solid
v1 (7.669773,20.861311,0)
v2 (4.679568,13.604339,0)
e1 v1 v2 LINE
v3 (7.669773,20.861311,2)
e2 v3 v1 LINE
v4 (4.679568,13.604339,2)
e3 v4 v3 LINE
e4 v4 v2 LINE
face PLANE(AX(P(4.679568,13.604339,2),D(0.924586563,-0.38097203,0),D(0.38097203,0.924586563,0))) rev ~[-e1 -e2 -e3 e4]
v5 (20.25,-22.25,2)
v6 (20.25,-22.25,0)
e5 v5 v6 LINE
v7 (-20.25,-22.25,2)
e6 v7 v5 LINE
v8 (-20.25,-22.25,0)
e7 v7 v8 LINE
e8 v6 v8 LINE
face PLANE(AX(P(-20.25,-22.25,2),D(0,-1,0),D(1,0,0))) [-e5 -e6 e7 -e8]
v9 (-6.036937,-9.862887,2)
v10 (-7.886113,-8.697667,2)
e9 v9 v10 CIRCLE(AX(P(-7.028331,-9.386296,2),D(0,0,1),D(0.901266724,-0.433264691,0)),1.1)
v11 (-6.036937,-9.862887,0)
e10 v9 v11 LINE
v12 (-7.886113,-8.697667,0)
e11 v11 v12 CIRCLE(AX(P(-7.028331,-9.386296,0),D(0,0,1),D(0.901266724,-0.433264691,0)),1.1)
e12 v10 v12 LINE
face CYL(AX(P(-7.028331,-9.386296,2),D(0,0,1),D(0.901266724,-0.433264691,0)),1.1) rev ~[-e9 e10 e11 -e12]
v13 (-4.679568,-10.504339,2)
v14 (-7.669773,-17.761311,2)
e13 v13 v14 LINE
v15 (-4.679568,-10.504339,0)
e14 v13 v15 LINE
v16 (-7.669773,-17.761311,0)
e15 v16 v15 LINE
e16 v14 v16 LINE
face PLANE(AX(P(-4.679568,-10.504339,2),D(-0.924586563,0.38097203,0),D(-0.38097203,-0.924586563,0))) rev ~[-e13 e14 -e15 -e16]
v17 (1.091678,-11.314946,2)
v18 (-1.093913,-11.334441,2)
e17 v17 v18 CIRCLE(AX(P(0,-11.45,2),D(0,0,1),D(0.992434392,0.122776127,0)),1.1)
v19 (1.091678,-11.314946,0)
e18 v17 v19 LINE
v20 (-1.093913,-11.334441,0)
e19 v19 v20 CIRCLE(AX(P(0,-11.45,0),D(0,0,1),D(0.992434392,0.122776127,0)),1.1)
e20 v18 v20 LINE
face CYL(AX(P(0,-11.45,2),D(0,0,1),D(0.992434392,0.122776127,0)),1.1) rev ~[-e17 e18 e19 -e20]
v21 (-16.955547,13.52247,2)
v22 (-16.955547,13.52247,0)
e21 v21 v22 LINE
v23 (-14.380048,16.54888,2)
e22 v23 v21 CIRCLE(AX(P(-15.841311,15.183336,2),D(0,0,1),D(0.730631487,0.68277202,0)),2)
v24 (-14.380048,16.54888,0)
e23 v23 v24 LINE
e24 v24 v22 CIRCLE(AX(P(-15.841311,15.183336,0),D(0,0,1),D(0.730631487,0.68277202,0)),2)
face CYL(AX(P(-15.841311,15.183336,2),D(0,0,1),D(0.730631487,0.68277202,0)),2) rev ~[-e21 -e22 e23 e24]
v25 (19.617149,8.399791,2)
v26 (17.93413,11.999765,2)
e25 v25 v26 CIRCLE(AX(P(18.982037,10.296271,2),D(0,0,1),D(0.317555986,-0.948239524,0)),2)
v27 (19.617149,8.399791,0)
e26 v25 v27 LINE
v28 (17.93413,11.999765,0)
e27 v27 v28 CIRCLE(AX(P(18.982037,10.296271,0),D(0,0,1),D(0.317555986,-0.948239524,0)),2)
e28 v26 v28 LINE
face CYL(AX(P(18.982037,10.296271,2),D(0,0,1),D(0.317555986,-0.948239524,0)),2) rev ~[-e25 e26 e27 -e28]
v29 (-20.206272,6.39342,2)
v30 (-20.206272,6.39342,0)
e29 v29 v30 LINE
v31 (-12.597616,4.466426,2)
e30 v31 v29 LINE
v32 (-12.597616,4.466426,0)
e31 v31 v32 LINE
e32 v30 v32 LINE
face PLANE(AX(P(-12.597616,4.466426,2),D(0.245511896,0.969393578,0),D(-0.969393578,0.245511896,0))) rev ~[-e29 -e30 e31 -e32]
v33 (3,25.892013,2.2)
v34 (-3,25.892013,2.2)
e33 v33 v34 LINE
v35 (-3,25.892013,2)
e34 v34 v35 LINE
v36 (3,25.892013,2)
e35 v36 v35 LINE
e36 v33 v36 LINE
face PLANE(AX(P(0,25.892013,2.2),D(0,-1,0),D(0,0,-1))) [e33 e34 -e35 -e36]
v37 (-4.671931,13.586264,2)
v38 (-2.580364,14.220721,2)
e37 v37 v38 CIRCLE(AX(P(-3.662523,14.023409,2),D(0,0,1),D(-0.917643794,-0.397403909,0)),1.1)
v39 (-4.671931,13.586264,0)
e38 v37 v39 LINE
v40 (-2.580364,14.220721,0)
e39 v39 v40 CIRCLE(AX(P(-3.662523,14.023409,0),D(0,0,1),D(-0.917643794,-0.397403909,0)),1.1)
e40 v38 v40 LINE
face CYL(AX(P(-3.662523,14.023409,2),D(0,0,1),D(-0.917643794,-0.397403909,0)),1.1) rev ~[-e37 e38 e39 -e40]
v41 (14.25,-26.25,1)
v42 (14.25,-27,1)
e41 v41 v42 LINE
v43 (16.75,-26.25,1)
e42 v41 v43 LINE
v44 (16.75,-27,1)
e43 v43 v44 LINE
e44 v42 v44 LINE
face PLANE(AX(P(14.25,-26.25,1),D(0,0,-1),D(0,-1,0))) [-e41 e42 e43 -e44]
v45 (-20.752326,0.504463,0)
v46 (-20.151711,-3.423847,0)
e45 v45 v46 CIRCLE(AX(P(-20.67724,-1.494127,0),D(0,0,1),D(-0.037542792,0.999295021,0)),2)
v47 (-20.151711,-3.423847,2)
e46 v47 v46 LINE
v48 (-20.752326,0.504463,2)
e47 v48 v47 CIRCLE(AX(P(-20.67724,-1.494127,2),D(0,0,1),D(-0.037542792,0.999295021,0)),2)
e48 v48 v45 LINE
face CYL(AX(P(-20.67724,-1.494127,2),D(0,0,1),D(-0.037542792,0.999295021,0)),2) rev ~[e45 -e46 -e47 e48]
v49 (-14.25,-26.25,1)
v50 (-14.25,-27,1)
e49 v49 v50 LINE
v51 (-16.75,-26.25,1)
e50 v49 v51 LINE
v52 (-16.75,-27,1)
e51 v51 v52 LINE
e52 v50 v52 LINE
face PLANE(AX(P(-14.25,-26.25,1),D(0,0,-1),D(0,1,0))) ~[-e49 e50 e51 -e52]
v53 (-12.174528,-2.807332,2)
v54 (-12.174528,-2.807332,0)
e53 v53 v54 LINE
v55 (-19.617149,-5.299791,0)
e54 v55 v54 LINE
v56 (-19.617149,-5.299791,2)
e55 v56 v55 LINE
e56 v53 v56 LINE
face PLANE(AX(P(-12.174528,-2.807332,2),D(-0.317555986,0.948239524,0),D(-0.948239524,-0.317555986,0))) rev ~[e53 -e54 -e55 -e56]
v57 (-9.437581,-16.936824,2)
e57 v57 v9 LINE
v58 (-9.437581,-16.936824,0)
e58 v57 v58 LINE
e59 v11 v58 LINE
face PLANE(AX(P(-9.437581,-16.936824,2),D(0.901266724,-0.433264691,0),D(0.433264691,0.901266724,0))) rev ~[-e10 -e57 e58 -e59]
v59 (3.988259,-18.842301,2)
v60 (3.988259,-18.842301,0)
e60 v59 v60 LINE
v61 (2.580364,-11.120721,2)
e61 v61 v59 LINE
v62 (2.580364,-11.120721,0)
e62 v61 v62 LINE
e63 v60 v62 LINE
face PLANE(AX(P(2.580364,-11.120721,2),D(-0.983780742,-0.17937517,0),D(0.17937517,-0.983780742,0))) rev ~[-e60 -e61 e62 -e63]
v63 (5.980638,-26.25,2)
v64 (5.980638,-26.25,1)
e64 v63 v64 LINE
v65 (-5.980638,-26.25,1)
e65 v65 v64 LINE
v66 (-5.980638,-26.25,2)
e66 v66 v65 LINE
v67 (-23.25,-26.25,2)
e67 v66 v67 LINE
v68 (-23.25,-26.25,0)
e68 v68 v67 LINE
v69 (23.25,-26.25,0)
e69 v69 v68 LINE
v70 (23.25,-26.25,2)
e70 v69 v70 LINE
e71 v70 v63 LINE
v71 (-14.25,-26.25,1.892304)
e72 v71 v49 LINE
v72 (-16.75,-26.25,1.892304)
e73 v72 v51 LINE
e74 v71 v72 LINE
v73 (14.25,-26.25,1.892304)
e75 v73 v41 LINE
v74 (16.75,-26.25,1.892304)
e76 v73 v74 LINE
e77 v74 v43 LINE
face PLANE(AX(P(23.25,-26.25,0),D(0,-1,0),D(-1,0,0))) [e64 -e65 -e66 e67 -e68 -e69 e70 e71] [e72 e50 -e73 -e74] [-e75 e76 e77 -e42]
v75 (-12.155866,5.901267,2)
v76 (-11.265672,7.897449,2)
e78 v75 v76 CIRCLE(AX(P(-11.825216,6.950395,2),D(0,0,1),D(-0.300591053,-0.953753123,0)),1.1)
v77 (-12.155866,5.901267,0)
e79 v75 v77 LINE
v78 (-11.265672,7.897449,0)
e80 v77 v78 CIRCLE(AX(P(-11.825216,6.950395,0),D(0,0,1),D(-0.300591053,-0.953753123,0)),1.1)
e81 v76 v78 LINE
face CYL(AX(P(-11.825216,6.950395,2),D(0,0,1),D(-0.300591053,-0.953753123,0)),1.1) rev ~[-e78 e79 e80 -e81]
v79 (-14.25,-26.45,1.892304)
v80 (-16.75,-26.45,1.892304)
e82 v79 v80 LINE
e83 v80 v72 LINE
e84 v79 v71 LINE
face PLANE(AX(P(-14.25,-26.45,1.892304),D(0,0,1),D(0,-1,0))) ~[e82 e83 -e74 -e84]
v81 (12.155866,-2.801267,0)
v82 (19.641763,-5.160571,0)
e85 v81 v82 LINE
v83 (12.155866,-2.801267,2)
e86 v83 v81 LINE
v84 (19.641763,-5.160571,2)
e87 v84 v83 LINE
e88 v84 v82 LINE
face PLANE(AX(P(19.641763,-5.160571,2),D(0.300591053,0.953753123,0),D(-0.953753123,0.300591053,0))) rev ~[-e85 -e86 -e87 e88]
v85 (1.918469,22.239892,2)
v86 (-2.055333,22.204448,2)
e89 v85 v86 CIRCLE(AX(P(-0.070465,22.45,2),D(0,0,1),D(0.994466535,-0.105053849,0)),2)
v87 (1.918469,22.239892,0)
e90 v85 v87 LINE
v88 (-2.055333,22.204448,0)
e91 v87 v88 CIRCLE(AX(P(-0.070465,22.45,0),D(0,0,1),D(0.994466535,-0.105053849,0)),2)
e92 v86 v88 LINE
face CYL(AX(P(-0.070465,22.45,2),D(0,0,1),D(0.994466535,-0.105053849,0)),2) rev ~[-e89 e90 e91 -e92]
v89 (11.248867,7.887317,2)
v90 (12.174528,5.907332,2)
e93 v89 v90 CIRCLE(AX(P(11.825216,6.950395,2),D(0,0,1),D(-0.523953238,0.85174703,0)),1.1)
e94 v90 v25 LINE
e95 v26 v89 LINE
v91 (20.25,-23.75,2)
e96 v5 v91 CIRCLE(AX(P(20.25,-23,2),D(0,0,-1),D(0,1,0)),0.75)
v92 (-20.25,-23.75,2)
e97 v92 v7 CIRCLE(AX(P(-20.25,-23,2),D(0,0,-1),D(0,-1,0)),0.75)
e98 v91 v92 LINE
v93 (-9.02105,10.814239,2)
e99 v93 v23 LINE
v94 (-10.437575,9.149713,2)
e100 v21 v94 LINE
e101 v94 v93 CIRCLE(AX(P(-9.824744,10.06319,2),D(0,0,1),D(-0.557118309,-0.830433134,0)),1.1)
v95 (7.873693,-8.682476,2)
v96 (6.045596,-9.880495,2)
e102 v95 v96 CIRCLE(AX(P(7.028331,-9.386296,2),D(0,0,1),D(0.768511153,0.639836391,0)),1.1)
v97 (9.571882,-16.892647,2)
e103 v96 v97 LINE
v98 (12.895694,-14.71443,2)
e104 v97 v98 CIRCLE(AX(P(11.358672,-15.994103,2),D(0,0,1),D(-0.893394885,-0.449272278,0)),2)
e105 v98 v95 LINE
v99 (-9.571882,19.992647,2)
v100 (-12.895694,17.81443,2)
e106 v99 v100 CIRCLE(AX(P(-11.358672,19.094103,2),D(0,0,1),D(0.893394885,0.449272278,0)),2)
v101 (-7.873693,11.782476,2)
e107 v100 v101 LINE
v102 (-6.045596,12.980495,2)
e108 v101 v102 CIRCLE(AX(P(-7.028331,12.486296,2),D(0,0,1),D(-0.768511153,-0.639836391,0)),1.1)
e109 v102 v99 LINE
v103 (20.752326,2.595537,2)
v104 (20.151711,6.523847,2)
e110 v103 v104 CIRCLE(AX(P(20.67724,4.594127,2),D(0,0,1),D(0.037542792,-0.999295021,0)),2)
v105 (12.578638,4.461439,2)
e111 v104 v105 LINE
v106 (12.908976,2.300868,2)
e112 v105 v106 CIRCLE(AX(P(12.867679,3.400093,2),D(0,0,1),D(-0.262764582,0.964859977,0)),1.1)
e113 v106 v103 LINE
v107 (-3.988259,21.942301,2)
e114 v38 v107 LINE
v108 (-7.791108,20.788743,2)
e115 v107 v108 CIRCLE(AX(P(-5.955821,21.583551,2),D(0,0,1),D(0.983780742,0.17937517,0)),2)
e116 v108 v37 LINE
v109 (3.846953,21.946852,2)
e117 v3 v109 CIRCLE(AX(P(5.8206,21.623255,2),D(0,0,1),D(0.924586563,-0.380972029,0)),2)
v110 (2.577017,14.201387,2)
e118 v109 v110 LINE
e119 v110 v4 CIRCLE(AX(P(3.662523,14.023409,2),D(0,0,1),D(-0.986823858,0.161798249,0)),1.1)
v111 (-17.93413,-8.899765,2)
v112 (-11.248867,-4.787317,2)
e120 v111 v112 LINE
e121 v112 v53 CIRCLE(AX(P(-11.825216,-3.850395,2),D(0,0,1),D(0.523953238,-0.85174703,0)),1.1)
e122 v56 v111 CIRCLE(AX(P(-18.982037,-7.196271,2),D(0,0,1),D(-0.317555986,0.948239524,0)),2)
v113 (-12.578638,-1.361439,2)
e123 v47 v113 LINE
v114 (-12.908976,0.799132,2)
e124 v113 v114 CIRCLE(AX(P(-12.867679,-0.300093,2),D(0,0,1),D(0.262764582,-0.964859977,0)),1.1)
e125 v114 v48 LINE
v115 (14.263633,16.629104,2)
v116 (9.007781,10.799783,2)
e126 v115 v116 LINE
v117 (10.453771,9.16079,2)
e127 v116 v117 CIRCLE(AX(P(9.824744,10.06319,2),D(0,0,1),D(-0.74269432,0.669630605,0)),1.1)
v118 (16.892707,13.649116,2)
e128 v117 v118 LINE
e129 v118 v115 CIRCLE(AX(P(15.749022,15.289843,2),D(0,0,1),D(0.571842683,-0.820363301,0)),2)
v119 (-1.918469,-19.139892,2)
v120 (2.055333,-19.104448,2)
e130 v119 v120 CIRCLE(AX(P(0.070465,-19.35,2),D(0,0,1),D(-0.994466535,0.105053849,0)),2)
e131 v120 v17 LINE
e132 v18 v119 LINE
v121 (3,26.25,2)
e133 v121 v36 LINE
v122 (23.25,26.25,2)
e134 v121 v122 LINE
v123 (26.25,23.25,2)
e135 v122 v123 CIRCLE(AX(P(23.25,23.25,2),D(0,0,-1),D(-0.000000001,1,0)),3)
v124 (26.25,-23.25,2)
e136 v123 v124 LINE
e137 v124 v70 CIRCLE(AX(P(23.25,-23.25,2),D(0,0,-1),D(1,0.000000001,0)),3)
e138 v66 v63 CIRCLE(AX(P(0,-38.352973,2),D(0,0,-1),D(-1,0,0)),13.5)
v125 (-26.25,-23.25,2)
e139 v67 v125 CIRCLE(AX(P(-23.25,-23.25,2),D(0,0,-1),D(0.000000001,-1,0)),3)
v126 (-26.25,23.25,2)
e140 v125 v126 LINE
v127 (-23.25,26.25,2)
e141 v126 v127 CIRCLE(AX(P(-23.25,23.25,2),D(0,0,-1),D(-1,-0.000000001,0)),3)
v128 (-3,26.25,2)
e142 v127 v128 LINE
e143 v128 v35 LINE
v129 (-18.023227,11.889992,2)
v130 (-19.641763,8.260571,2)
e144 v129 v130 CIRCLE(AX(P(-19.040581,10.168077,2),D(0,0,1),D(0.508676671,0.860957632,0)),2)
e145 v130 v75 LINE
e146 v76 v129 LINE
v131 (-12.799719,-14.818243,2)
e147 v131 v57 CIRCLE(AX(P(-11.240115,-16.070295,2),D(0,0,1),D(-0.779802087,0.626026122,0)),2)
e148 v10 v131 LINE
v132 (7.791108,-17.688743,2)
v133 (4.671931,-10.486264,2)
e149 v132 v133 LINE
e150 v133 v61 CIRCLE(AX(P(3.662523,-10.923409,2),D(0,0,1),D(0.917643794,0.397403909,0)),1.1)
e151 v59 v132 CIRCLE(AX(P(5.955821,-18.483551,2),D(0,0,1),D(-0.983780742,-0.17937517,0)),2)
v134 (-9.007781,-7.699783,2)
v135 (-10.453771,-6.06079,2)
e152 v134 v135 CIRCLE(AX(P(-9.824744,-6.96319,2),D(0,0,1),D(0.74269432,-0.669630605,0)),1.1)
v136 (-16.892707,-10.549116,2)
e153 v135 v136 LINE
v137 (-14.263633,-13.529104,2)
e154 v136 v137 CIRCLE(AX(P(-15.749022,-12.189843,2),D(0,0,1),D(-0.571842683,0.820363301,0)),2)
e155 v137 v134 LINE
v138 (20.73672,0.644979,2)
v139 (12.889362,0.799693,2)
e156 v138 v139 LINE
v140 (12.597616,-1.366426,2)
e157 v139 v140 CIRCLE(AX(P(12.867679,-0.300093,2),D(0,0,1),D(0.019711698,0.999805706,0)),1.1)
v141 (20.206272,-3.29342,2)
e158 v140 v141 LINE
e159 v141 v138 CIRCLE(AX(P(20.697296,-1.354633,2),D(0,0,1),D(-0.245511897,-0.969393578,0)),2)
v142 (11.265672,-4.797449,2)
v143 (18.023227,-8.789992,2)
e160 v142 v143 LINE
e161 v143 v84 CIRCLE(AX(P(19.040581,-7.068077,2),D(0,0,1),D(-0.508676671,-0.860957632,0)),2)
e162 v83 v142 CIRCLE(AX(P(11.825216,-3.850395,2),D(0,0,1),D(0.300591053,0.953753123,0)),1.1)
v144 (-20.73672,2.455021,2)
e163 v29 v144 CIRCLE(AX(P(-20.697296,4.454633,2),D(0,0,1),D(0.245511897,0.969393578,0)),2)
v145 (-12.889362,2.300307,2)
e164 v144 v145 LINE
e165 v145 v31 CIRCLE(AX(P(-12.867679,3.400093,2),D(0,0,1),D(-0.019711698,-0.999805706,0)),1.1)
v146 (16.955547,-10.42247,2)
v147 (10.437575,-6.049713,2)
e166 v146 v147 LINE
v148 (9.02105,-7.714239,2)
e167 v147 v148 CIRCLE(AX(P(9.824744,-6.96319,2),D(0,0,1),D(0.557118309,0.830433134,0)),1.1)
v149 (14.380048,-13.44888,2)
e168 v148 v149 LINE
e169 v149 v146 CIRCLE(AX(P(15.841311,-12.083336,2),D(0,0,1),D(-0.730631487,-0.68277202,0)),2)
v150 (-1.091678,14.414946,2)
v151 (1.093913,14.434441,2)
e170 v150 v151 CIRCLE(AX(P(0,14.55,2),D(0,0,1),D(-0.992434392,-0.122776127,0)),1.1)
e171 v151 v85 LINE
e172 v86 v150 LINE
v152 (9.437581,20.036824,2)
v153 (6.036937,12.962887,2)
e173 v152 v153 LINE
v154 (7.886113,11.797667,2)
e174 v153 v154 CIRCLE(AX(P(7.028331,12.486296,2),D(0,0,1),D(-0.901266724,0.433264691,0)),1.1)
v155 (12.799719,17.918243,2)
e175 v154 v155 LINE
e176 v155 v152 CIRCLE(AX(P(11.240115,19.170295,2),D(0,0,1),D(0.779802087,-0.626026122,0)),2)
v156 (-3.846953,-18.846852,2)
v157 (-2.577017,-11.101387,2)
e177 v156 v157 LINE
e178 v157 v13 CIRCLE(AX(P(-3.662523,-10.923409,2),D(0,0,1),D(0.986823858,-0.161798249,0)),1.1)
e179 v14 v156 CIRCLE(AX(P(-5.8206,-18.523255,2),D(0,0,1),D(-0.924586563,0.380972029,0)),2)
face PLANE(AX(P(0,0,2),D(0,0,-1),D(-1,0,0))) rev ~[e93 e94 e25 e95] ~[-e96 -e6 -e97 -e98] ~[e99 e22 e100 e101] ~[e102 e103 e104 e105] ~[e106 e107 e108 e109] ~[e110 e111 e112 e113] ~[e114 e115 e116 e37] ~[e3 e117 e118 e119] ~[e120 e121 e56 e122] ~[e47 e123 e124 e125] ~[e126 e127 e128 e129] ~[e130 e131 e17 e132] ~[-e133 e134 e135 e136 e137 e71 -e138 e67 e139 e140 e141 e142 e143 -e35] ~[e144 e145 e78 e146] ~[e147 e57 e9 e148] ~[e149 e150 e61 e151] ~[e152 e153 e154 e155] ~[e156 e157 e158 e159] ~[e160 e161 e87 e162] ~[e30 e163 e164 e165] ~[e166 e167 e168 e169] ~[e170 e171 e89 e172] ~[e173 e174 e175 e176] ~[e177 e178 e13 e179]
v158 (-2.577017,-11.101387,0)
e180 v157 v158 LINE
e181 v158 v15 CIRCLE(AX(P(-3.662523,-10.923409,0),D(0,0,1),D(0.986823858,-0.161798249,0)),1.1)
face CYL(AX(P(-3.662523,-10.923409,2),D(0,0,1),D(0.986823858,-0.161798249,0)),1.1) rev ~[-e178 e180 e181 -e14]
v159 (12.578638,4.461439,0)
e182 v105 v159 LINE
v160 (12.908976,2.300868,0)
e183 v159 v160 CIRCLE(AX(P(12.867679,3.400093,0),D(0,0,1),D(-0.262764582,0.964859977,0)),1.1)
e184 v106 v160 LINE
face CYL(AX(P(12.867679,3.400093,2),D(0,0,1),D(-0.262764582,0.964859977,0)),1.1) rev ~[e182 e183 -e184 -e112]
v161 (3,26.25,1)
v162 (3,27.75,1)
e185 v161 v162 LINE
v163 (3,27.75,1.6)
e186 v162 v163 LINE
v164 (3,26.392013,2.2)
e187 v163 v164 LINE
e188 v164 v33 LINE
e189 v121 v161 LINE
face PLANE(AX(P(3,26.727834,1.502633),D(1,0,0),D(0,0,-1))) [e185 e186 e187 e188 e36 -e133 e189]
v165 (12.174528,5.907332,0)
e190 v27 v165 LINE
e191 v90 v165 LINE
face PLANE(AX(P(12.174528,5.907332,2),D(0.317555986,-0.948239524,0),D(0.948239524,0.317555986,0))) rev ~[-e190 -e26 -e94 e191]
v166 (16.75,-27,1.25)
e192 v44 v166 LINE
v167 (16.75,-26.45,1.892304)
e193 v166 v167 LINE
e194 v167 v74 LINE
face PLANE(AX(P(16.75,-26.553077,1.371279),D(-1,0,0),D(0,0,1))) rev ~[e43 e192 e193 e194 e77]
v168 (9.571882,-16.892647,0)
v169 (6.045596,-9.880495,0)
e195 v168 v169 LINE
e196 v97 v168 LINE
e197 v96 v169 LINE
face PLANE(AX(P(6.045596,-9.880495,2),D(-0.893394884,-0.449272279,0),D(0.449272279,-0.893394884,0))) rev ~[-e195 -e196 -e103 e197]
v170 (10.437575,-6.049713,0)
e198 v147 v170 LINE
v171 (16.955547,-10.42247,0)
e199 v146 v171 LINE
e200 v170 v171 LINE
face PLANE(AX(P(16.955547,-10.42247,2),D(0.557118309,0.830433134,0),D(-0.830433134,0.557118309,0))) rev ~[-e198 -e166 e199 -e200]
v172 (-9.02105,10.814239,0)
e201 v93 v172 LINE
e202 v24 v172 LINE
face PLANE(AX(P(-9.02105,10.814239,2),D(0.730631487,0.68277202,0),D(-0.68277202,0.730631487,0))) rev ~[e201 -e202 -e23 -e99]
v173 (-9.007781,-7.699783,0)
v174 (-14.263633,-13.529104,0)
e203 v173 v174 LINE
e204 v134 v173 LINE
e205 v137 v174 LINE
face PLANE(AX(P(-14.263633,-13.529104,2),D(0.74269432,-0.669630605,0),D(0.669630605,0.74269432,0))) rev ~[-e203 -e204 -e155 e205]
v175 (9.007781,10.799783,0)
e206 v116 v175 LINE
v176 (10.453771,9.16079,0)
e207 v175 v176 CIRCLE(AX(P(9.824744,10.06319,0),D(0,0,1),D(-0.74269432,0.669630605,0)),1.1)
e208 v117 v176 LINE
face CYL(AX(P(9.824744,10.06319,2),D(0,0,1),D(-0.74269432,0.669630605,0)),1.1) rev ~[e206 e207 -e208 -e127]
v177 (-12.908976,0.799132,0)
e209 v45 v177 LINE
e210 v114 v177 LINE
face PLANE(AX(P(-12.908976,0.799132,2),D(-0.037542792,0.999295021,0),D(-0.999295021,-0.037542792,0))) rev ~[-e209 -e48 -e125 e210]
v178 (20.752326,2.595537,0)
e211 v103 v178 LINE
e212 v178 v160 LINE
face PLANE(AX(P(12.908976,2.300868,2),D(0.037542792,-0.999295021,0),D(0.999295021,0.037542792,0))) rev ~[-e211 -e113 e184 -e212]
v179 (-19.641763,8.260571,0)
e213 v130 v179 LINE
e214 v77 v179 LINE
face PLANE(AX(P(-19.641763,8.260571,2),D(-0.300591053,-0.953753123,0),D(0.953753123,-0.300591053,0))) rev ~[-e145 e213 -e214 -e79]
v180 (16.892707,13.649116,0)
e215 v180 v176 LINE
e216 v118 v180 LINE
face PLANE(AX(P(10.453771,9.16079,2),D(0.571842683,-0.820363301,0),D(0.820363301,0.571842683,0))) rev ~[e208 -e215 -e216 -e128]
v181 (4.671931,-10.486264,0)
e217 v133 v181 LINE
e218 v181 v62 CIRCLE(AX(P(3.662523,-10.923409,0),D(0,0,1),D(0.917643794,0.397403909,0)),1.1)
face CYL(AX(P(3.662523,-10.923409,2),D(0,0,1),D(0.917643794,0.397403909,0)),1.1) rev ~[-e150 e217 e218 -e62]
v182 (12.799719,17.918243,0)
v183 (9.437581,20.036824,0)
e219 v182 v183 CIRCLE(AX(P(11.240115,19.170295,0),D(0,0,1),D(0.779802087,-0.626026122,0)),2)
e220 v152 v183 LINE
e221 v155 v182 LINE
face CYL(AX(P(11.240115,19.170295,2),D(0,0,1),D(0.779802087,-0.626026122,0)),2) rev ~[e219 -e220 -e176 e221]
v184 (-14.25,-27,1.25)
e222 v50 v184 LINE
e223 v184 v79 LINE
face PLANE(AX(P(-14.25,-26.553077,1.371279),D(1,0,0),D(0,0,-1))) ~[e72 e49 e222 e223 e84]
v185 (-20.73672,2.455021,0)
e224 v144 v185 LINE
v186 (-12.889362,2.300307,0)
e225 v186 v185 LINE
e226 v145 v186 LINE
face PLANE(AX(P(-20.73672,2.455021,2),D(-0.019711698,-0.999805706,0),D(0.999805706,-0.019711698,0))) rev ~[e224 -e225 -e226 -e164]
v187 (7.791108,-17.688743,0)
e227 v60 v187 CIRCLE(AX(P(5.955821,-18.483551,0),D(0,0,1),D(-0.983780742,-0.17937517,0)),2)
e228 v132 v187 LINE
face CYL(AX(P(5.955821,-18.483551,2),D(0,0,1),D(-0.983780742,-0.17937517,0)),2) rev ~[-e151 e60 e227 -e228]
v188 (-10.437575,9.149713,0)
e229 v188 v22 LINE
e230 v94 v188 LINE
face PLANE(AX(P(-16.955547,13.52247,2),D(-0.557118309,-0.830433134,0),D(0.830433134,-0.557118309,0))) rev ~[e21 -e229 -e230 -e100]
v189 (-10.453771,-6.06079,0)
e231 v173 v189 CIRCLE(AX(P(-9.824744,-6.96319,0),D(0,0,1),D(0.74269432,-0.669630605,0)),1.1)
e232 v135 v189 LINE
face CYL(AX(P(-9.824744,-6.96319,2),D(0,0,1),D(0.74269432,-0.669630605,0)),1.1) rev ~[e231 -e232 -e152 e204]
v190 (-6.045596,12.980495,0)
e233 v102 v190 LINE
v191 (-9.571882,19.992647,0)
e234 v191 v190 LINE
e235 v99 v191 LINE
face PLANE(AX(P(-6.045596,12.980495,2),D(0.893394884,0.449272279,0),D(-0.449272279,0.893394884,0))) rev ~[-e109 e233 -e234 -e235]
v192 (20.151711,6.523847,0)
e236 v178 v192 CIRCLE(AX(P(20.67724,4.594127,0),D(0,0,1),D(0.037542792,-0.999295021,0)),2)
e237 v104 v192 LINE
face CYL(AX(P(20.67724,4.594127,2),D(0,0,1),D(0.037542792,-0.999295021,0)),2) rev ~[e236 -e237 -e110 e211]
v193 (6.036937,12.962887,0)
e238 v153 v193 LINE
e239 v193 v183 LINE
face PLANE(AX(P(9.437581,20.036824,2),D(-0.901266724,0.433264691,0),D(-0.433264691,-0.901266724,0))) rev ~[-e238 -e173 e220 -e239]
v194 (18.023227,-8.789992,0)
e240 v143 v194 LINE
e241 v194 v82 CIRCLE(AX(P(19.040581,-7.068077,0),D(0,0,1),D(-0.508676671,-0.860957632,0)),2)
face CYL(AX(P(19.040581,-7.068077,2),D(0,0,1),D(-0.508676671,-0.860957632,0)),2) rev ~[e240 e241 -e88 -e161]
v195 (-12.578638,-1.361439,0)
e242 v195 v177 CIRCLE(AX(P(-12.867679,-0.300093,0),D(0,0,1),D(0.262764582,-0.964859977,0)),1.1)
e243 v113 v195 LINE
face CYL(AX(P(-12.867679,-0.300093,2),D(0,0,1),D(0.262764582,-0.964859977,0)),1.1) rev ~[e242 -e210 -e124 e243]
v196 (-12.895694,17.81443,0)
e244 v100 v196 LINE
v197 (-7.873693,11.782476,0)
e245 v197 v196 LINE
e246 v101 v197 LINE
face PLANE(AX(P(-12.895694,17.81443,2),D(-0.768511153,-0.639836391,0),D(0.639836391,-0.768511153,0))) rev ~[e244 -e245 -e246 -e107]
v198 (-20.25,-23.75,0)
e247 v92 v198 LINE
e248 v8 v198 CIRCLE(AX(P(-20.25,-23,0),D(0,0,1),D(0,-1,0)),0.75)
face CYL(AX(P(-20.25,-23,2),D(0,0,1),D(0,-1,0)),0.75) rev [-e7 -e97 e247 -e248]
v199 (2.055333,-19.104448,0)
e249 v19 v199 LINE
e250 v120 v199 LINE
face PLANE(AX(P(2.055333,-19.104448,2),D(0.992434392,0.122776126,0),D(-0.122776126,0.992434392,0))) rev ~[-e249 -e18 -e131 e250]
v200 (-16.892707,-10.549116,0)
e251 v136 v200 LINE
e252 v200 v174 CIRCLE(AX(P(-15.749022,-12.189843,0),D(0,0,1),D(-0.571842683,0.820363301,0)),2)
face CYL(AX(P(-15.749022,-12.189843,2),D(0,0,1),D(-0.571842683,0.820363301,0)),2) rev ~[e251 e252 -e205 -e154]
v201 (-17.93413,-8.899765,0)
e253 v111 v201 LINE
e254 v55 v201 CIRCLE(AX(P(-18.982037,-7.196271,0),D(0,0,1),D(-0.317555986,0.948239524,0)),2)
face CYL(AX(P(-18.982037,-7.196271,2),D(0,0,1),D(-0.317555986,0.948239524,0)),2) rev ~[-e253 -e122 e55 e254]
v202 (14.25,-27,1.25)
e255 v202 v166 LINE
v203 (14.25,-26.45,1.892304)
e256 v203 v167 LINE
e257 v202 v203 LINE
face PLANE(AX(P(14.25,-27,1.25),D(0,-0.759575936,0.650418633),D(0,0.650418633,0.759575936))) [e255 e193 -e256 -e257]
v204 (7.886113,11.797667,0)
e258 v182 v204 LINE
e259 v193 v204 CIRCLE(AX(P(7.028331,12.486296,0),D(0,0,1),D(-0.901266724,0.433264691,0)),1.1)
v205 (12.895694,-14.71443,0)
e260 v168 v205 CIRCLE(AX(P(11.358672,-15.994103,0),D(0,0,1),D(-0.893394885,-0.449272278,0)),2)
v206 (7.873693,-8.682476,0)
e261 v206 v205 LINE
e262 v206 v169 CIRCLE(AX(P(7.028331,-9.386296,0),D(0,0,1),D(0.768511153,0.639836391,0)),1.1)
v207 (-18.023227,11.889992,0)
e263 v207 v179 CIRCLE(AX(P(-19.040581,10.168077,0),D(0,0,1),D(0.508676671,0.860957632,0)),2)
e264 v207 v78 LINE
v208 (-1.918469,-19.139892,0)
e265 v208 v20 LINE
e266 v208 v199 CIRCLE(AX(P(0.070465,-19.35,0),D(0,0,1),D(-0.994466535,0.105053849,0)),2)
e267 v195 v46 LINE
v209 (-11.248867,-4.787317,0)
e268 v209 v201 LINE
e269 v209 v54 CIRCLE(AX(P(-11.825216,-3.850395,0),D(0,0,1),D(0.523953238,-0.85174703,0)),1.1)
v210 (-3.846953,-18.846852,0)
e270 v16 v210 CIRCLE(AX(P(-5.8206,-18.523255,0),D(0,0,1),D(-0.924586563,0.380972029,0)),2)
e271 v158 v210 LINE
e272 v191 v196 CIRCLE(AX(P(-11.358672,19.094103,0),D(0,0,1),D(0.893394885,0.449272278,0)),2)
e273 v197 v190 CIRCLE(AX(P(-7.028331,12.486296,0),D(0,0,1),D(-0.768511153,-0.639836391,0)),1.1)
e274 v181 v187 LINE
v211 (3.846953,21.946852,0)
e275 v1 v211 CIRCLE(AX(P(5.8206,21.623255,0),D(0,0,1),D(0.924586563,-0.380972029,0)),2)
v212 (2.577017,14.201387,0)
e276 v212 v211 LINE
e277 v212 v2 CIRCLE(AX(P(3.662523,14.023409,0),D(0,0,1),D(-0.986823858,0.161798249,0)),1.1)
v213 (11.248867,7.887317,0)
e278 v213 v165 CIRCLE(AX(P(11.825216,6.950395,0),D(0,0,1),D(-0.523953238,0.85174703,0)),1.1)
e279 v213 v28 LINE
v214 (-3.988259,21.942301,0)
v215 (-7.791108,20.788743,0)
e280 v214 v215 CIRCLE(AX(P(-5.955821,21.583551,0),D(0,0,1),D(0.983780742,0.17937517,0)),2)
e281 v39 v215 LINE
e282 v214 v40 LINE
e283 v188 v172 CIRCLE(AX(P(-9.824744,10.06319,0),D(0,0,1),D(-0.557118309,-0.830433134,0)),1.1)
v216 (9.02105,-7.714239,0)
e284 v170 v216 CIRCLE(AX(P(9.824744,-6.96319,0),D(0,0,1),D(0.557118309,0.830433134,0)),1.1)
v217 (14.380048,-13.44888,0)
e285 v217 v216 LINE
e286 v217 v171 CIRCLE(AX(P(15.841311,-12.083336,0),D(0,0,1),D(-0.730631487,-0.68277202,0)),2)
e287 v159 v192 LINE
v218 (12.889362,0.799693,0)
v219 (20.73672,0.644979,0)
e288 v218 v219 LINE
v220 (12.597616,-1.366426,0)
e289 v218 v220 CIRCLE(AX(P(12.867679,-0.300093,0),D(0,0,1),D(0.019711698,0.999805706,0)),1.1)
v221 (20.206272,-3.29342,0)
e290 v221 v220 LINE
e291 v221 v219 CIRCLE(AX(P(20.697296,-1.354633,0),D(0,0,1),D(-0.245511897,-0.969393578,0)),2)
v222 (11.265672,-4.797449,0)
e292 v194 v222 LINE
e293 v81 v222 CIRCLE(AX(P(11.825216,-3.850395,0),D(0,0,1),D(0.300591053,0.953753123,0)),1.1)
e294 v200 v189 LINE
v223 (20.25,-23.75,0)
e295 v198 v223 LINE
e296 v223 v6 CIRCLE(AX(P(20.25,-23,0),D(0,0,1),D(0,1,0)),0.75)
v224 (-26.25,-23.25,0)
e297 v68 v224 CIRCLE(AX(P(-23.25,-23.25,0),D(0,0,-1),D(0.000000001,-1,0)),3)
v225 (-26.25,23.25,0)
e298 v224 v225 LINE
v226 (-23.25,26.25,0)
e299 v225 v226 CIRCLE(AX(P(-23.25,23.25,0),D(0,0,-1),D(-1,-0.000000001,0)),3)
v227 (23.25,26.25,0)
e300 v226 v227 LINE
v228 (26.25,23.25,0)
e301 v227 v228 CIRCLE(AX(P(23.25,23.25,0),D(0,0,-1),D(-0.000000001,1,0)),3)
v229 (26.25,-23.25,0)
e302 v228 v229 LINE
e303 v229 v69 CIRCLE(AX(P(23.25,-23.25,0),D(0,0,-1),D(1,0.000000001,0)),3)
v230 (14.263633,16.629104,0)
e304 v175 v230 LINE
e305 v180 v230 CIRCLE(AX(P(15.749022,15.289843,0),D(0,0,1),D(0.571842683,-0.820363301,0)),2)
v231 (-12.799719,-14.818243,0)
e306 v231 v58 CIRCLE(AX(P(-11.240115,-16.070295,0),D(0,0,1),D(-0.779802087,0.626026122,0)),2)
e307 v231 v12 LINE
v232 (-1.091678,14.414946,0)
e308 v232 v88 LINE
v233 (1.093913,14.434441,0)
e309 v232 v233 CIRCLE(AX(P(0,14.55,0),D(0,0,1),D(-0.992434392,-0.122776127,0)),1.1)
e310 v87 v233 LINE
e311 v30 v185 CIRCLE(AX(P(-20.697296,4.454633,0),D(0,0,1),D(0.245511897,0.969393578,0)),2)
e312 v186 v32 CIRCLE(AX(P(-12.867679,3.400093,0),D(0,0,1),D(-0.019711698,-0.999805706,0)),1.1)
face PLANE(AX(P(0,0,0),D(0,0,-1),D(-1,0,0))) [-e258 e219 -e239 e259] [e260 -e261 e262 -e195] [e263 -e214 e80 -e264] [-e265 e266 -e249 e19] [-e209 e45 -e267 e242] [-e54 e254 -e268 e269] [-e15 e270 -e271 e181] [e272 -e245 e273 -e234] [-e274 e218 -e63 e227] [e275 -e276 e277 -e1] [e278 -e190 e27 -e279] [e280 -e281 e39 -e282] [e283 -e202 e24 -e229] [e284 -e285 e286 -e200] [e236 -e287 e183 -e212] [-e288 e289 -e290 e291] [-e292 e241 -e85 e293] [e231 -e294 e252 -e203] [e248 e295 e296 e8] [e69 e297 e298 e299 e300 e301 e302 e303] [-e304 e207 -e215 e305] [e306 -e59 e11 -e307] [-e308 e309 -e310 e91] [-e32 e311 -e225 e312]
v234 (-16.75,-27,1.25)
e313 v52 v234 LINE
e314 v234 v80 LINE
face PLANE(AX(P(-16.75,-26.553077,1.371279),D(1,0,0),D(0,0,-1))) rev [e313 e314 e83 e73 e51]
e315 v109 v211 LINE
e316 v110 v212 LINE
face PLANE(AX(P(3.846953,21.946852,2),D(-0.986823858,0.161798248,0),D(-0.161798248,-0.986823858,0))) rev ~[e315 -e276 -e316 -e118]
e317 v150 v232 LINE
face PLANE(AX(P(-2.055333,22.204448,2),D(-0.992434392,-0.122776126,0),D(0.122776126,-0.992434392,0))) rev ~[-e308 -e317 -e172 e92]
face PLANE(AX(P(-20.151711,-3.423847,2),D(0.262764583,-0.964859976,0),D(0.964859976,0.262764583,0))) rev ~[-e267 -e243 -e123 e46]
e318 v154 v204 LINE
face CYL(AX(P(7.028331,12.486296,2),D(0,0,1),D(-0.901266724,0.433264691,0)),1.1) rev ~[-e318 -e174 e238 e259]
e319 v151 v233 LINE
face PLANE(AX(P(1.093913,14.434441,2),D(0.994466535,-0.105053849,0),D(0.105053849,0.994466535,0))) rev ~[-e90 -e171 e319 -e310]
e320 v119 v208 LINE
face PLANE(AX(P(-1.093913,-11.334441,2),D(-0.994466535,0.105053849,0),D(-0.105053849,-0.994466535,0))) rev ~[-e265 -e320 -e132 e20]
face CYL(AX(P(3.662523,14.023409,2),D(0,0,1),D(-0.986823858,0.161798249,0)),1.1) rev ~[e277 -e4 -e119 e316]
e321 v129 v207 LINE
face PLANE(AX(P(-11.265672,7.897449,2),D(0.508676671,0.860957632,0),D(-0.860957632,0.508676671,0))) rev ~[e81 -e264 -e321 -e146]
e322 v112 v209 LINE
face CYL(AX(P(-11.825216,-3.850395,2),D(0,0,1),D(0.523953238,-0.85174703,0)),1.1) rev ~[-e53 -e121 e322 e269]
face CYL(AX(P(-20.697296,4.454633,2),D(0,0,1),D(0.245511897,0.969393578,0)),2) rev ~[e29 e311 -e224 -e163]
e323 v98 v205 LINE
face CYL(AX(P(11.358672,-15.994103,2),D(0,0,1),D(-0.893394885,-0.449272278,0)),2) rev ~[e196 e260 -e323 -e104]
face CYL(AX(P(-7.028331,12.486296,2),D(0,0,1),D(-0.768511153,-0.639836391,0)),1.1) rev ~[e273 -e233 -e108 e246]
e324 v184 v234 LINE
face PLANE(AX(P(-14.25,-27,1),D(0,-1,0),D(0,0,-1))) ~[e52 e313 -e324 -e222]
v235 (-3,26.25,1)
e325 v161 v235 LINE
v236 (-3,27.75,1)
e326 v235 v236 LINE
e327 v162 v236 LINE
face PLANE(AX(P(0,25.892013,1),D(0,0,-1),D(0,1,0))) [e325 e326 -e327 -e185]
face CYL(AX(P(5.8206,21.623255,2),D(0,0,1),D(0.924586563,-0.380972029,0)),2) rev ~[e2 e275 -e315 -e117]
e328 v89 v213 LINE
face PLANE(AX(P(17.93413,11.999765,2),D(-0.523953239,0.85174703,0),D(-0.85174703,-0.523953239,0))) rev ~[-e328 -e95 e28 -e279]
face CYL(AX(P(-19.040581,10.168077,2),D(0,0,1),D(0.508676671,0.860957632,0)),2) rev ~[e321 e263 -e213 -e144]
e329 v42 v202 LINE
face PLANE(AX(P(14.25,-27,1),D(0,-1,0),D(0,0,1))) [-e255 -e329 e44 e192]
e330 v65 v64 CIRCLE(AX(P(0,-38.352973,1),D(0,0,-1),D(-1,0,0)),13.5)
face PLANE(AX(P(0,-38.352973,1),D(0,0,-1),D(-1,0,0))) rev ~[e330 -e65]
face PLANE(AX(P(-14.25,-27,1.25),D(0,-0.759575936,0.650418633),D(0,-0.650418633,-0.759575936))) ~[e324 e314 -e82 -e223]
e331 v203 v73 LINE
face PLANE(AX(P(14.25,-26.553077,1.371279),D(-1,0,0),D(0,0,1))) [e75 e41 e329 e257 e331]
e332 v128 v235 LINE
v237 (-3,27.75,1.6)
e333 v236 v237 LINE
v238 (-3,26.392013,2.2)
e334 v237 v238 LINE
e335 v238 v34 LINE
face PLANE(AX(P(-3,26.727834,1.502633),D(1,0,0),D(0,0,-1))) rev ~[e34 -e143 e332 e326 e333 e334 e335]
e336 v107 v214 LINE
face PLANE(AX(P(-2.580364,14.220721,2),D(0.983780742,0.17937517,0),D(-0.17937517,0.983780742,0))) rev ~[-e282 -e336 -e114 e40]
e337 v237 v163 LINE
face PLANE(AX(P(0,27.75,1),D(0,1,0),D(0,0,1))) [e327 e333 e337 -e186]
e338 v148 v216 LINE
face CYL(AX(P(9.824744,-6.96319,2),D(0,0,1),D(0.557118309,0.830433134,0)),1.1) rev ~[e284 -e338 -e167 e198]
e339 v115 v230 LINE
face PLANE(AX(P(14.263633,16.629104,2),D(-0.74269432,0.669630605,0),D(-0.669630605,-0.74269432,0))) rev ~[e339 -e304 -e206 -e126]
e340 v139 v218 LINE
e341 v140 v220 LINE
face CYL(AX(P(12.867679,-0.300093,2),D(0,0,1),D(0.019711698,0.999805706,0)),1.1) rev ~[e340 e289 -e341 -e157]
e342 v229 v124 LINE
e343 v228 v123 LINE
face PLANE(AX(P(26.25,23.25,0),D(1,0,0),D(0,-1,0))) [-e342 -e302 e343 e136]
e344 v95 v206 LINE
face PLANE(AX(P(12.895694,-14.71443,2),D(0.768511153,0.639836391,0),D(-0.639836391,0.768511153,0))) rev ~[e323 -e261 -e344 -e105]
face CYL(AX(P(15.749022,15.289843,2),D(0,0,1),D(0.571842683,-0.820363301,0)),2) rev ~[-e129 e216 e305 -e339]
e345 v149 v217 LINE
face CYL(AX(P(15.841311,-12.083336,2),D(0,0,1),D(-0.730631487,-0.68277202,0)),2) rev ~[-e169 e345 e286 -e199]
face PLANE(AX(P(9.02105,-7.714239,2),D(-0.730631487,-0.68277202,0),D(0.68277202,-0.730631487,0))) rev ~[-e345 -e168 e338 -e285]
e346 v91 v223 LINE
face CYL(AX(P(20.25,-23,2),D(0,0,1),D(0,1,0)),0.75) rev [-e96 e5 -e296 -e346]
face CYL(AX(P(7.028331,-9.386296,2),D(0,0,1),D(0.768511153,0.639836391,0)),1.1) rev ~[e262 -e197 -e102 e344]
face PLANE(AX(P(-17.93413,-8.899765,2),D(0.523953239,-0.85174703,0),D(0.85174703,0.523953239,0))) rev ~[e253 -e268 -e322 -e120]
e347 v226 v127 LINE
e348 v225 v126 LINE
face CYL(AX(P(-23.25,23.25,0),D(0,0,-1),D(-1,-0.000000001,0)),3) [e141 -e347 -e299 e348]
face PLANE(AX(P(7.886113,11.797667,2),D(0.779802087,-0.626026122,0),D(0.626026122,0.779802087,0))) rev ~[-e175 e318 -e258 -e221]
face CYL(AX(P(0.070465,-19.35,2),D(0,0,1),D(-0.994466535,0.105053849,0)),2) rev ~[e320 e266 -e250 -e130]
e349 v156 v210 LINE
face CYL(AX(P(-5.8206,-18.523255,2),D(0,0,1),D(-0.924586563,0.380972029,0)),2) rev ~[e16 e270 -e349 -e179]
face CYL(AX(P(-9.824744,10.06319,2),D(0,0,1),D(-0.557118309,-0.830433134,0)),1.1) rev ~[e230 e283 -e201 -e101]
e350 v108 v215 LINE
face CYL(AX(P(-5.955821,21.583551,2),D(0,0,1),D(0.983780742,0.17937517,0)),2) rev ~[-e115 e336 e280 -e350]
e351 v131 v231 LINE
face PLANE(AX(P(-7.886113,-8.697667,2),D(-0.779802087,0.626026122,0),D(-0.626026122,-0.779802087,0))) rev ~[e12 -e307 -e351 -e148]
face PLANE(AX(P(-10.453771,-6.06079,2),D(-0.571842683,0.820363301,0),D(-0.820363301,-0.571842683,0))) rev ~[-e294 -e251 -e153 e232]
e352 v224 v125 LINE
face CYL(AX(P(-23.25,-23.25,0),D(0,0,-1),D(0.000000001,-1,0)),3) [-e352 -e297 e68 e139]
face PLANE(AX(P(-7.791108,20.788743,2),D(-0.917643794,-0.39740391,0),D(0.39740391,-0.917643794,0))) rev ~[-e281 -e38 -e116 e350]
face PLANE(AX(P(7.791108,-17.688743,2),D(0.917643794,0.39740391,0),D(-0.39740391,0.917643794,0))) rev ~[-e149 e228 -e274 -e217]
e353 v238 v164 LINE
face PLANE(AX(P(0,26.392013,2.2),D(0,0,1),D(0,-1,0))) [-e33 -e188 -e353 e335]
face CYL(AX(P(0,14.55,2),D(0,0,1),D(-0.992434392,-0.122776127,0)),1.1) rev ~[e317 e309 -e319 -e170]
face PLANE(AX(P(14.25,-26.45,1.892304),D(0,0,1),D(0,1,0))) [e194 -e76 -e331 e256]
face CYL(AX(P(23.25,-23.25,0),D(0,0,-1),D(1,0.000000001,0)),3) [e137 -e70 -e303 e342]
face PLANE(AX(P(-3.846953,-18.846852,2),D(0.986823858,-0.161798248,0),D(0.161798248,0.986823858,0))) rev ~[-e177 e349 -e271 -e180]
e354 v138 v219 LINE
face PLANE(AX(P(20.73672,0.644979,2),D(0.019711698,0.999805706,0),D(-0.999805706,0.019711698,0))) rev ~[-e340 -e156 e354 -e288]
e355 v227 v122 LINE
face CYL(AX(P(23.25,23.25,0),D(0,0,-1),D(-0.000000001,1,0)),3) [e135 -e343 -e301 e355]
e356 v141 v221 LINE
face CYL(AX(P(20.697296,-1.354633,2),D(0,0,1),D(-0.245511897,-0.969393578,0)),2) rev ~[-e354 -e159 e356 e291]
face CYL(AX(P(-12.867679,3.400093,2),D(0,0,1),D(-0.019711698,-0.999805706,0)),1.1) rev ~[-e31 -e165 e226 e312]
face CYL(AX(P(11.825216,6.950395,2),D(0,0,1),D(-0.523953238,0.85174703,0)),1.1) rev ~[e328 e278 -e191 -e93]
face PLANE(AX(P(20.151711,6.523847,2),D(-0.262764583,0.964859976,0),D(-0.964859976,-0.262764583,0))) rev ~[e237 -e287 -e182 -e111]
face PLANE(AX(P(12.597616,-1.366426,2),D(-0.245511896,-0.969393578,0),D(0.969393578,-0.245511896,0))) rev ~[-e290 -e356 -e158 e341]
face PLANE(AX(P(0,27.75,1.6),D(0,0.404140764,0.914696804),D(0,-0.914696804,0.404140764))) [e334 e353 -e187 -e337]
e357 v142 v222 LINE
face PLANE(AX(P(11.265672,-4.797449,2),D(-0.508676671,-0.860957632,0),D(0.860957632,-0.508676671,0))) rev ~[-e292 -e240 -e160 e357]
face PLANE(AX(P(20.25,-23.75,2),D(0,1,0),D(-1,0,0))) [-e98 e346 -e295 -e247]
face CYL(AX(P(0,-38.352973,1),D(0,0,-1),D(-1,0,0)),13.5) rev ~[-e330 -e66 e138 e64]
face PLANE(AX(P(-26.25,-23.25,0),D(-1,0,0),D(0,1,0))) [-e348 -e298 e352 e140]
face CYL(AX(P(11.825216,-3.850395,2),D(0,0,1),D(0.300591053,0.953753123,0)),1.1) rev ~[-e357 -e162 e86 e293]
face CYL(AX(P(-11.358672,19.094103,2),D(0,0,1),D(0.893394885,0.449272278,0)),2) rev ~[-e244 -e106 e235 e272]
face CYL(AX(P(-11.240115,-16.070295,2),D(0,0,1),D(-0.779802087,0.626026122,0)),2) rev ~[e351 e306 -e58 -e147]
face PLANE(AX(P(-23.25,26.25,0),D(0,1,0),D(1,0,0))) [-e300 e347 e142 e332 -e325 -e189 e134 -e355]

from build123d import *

# Parameters (mm, degrees)
BOSS_EXTRUDE1_DEPTH = 2
CUT_EXTRUDE1_DEPTH  = 12
CUT_EXTRUDE2_START  = -1
SKETCH3_R           = 13.5
CUT_EXTRUDE2_DEPTH  = 1
BOSS_EXTRUDE2_START = 14.25
BOSS_EXTRUDE2_DEPTH = 2.5
BOSS_EXTRUDE3_DEPTH = 3


with BuildPart() as part:
    # Sketch1 → Boss-Extrude1 (new body)
    with BuildSketch(Plane.XY):
        with BuildLine():
            Line((-23.25, 26.25), (23.25, 26.25))
            ThreePointArc((23.25, 26.25), (25.371320344, 25.371320344), (26.25, 23.25))
            Line((26.25, 23.25), (26.25, -23.25))
            ThreePointArc((26.25, -23.25), (25.371320344, -25.371320344), (23.25, -26.25))
            Line((23.25, -26.25), (-23.25, -26.25))
            ThreePointArc((-23.25, -26.25), (-25.371320344, -25.371320344), (-26.25, -23.25))
            Line((-26.25, -23.25), (-26.25, 23.25))
            ThreePointArc((-26.25, 23.25), (-25.371320344, 25.371320344), (-23.25, 26.25))
        make_face()
    extrude(amount=BOSS_EXTRUDE1_DEPTH)

    # Sketch2 → Cut-Extrude1 (cut)
    with BuildSketch(Plane.XY.offset(2)):
        with BuildLine():
            Line((-20.25, -22.25), (20.25, -22.25))
            ThreePointArc((20.25, -22.25), (21, -23), (20.25, -23.75))
            Line((20.25, -23.75), (-20.25, -23.75))
            ThreePointArc((-20.25, -23.75), (-21, -23), (-20.25, -22.25))
        make_face()
        with BuildLine():
            Line((-2.05533329, 22.204447747), (-1.091677831, 14.414946261))
            ThreePointArc((-1.091677831, 14.414946261), (0.009811123, 13.450043755), (1.093913188, 14.434440766))
            Line((1.093913188, 14.434440766), (1.918468564, 22.239892302))
            ThreePointArc((1.918468564, 22.239892302), (-0.088302912, 24.449920446), (-2.05533329, 22.204447747))
        make_face()
        with BuildLine():
            Line((3.846952523, 21.94685179), (2.577016995, 14.20138673))
            ThreePointArc((2.577016995, 14.20138673), (3.362043457, 12.965244255), (4.679568458, 13.604339425))
            Line((4.679568458, 13.604339425), (7.669773366, 20.861311235))
            ThreePointArc((7.669773366, 20.861311235), (6.366927115, 23.54719057), (3.846952523, 21.94685179))
        make_face()
        with BuildLine():
            Line((9.437581122, 20.036824206), (6.036937231, 12.962887087))
            ThreePointArc((6.036937231, 12.962887087), (6.441903025, 11.555649556), (7.886112922, 11.797667193))
            Line((7.886112922, 11.797667193), (12.799718744, 17.91824258))
            ThreePointArc((12.799718744, 17.91824258), (12.306346573, 20.862379135), (9.437581122, 20.036824206))
        make_face()
        with BuildLine():
            Line((14.263633026, 16.62910407), (9.007780715, 10.799783207))
            ThreePointArc((9.007780715, 10.799783207), (8.999877922, 9.335456635), (10.453771418, 9.16078991))
            Line((10.453771418, 9.16078991), (16.892707032, 13.649116258))
            ThreePointArc((16.892707032, 13.649116258), (17.24877902, 16.612993599), (14.263633026, 16.62910407))
        make_face()
        with BuildLine():
            Line((17.934130212, 11.999764601), (11.248867377, 7.887316902))
            ThreePointArc((11.248867377, 7.887316902), (10.828736233, 6.484532319), (12.174527524, 5.907331692))
            Line((12.174527524, 5.907331692), (19.617148662, 8.399791492))
            ThreePointArc((19.617148662, 8.399791492), (20.793817974, 11.143293904), (17.934130212, 11.999764601))
        make_face()
        with BuildLine():
            Line((20.151710825, 6.523847352), (12.578637704, 4.461438872))
            ThreePointArc((12.578637704, 4.461438872), (11.780314736, 3.233841542), (12.908975815, 2.300868375))
            Line((12.908975815, 2.300868375), (20.752325574, 2.595537357))
            ThreePointArc((20.752325574, 2.595537357), (22.65426546, 4.89640259), (20.151710825, 6.523847352))
        make_face()
        with BuildLine():
            Line((20.736719675, 0.64497857), (12.889361612, 0.799693379))
            ThreePointArc((12.889361612, 0.799693379), (11.777522199, -0.153264063), (12.597615658, -1.366425833))
            Line((12.597615658, -1.366425833), (20.206272487, -3.293419997))
            ThreePointArc((20.206272487, -3.293419997), (22.67939909, -1.621594359), (20.736719675, 0.64497857))
        make_face()
        with BuildLine():
            Line((19.641762823, -5.160570757), (12.155866098, -2.801266734))
            ThreePointArc((12.155866098, -2.801266734), (10.820584857, -3.402381343), (11.265671602, -4.797448565))
            Line((11.265671602, -4.797448565), (18.023227375, -8.789992267))
            ThreePointArc((18.023227375, -8.789992267), (20.867182684, -7.882647596), (19.641762823, -5.160570757))
        make_face()
        with BuildLine():
            Line((16.95554716, -10.422469552), (10.437574607, -6.049713094))
            ThreePointArc((10.437574607, -6.049713094), (8.987028083, -6.250286139), (9.021049831, -7.714238763))
            Line((9.021049831, -7.714238763), (14.380047569, -13.448879859))
            ThreePointArc((14.380047569, -13.448879859), (17.36443124, -13.379523823), (16.95554716, -10.422469552))
        make_face()
        with BuildLine():
            Line((12.895693906, -14.714430066), (7.873692895, -8.682475896))
            ThreePointArc((7.873692895, -8.682475896), (6.425395741, -8.466258143), (6.045596254, -9.880495433))
            Line((6.045596254, -9.880495433), (9.57188183, -16.892647405))
            ThreePointArc((9.57188183, -16.892647405), (12.454916846, -17.666898819), (12.895693906, -14.714430066))
        make_face()
        with BuildLine():
            Line((7.791108224, -17.688743184), (4.671931412, -10.486264357))
            ThreePointArc((4.671931412, -10.486264357), (3.34321605, -9.870772481), (2.580364423, -11.120721344))
            Line((2.580364423, -11.120721344), (3.988259152, -18.842301342))
            ThreePointArc((3.988259152, -18.842301342), (6.536379162, -20.397434959), (7.791108224, -17.688743184))
        make_face()
        with BuildLine():
            Line((2.05533329, -19.104447747), (1.091677831, -11.314946261))
            ThreePointArc((1.091677831, -11.314946261), (-0.009811123, -10.350043755), (-1.093913188, -11.334440766))
            Line((-1.093913188, -11.334440766), (-1.918468564, -19.139892302))
            ThreePointArc((-1.918468564, -19.139892302), (0.088302912, -21.349920446), (2.05533329, -19.104447747))
        make_face()
        with BuildLine():
            Line((-3.846952523, -18.84685179), (-2.577016995, -11.10138673))
            ThreePointArc((-2.577016995, -11.10138673), (-3.362043457, -9.865244255), (-4.679568458, -10.504339425))
            Line((-4.679568458, -10.504339425), (-7.669773366, -17.761311235))
            ThreePointArc((-7.669773366, -17.761311235), (-6.366927115, -20.44719057), (-3.846952523, -18.84685179))
        make_face()
        with BuildLine():
            Line((-9.437581122, -16.936824206), (-6.036937231, -9.862887087))
            ThreePointArc((-6.036937231, -9.862887087), (-6.441903025, -8.455649556), (-7.886112922, -8.697667193))
            Line((-7.886112922, -8.697667193), (-12.799718744, -14.81824258))
            ThreePointArc((-12.799718744, -14.81824258), (-12.306346573, -17.762379135), (-9.437581122, -16.936824206))
        make_face()
        with BuildLine():
            Line((-14.263633026, -13.52910407), (-9.007780715, -7.699783207))
            ThreePointArc((-9.007780715, -7.699783207), (-8.999877922, -6.235456635), (-10.453771418, -6.06078991))
            Line((-10.453771418, -6.06078991), (-16.892707032, -10.549116258))
            ThreePointArc((-16.892707032, -10.549116258), (-17.24877902, -13.512993599), (-14.263633026, -13.52910407))
        make_face()
        with BuildLine():
            Line((-17.934130212, -8.899764601), (-11.248867377, -4.787316902))
            ThreePointArc((-11.248867377, -4.787316902), (-10.828736233, -3.384532319), (-12.174527524, -2.807331692))
            Line((-12.174527524, -2.807331692), (-19.617148662, -5.299791492))
            ThreePointArc((-19.617148662, -5.299791492), (-20.793817974, -8.043293904), (-17.934130212, -8.899764601))
        make_face()
        with BuildLine():
            Line((-20.151710825, -3.423847352), (-12.578637704, -1.361438872))
            ThreePointArc((-12.578637704, -1.361438872), (-11.780314736, -0.133841542), (-12.908975815, 0.799131625))
            Line((-12.908975815, 0.799131625), (-20.752325574, 0.504462643))
            ThreePointArc((-20.752325574, 0.504462643), (-22.65426546, -1.79640259), (-20.151710825, -3.423847352))
        make_face()
        with BuildLine():
            Line((-20.736719675, 2.45502143), (-12.889361612, 2.300306621))
            ThreePointArc((-12.889361612, 2.300306621), (-11.777522199, 3.253264063), (-12.597615658, 4.466425833))
            Line((-12.597615658, 4.466425833), (-20.206272487, 6.393419997))
            ThreePointArc((-20.206272487, 6.393419997), (-22.67939909, 4.721594359), (-20.736719675, 2.45502143))
        make_face()
        with BuildLine():
            Line((-19.641762823, 8.260570757), (-12.155866098, 5.901266734))
            ThreePointArc((-12.155866098, 5.901266734), (-10.820584857, 6.502381343), (-11.265671602, 7.897448565))
            Line((-11.265671602, 7.897448565), (-18.023227375, 11.889992267))
            ThreePointArc((-18.023227375, 11.889992267), (-20.867182684, 10.982647596), (-19.641762823, 8.260570757))
        make_face()
        with BuildLine():
            Line((-16.95554716, 13.522469552), (-10.437574607, 9.149713094))
            ThreePointArc((-10.437574607, 9.149713094), (-8.987028083, 9.350286139), (-9.021049831, 10.814238763))
            Line((-9.021049831, 10.814238763), (-14.380047569, 16.548879859))
            ThreePointArc((-14.380047569, 16.548879859), (-17.36443124, 16.479523823), (-16.95554716, 13.522469552))
        make_face()
        with BuildLine():
            Line((-12.895693906, 17.814430066), (-7.873692895, 11.782475896))
            ThreePointArc((-7.873692895, 11.782475896), (-6.425395741, 11.566258143), (-6.045596254, 12.980495433))
            Line((-6.045596254, 12.980495433), (-9.57188183, 19.992647405))
            ThreePointArc((-9.57188183, 19.992647405), (-12.454916846, 20.766898819), (-12.895693906, 17.814430066))
        make_face()
        with BuildLine():
            Line((-7.791108224, 20.788743184), (-4.671931412, 13.586264357))
            ThreePointArc((-4.671931412, 13.586264357), (-3.34321605, 12.970772481), (-2.580364423, 14.220721344))
            Line((-2.580364423, 14.220721344), (-3.988259152, 21.942301342))
            ThreePointArc((-3.988259152, 21.942301342), (-6.536379162, 23.497434959), (-7.791108224, 20.788743184))
        make_face()
    extrude(amount=-CUT_EXTRUDE1_DEPTH, mode=Mode.SUBTRACT)

    # Sketch3 → Cut-Extrude2 (cut)
    with BuildSketch(Plane(origin=(0, 0, 0), x_dir=(-1, 0, 0), z_dir=(0, 0, -1)).offset(CUT_EXTRUDE2_START)):
        with Locations((0, -38.352973417)):
            Circle(SKETCH3_R)
    extrude(amount=-CUT_EXTRUDE2_DEPTH, mode=Mode.SUBTRACT)

    # Sketch4 → Boss-Extrude2 (add)
    with BuildSketch(Plane(origin=(0, 0, 0), x_dir=(0, 0, -1), z_dir=(1, 0, 0)).offset(BOSS_EXTRUDE2_START)):
        Polygon((-1, -26.25), (-1, -27), (-1.25, -27), (-1.892304423, -26.45), (-1.892304423, -26.25), align=None)
    boss_extrude2 = extrude(amount=BOSS_EXTRUDE2_DEPTH)

    # Mirror3: Boss-Extrude2 across plane
    add(boss_extrude2.mirror(Plane(origin=(0, 0, 0), x_dir=(0, 0, 1), z_dir=(1, 0, 0))))

    # Sketch5 → Boss-Extrude3 (add, symmetric)
    with BuildSketch(Plane(origin=(0, 0, 0), x_dir=(0, 0, -1), z_dir=(1, 0, 0))):
        Polygon((-1, 26.25), (-1, 27.75), (-1.6, 27.75), (-2.2, 26.392012559), (-2.2, 25.892012559), (-1, 25.892012559), align=None)
    extrude(amount=BOSS_EXTRUDE3_DEPTH, both=True)


solid = part.part
